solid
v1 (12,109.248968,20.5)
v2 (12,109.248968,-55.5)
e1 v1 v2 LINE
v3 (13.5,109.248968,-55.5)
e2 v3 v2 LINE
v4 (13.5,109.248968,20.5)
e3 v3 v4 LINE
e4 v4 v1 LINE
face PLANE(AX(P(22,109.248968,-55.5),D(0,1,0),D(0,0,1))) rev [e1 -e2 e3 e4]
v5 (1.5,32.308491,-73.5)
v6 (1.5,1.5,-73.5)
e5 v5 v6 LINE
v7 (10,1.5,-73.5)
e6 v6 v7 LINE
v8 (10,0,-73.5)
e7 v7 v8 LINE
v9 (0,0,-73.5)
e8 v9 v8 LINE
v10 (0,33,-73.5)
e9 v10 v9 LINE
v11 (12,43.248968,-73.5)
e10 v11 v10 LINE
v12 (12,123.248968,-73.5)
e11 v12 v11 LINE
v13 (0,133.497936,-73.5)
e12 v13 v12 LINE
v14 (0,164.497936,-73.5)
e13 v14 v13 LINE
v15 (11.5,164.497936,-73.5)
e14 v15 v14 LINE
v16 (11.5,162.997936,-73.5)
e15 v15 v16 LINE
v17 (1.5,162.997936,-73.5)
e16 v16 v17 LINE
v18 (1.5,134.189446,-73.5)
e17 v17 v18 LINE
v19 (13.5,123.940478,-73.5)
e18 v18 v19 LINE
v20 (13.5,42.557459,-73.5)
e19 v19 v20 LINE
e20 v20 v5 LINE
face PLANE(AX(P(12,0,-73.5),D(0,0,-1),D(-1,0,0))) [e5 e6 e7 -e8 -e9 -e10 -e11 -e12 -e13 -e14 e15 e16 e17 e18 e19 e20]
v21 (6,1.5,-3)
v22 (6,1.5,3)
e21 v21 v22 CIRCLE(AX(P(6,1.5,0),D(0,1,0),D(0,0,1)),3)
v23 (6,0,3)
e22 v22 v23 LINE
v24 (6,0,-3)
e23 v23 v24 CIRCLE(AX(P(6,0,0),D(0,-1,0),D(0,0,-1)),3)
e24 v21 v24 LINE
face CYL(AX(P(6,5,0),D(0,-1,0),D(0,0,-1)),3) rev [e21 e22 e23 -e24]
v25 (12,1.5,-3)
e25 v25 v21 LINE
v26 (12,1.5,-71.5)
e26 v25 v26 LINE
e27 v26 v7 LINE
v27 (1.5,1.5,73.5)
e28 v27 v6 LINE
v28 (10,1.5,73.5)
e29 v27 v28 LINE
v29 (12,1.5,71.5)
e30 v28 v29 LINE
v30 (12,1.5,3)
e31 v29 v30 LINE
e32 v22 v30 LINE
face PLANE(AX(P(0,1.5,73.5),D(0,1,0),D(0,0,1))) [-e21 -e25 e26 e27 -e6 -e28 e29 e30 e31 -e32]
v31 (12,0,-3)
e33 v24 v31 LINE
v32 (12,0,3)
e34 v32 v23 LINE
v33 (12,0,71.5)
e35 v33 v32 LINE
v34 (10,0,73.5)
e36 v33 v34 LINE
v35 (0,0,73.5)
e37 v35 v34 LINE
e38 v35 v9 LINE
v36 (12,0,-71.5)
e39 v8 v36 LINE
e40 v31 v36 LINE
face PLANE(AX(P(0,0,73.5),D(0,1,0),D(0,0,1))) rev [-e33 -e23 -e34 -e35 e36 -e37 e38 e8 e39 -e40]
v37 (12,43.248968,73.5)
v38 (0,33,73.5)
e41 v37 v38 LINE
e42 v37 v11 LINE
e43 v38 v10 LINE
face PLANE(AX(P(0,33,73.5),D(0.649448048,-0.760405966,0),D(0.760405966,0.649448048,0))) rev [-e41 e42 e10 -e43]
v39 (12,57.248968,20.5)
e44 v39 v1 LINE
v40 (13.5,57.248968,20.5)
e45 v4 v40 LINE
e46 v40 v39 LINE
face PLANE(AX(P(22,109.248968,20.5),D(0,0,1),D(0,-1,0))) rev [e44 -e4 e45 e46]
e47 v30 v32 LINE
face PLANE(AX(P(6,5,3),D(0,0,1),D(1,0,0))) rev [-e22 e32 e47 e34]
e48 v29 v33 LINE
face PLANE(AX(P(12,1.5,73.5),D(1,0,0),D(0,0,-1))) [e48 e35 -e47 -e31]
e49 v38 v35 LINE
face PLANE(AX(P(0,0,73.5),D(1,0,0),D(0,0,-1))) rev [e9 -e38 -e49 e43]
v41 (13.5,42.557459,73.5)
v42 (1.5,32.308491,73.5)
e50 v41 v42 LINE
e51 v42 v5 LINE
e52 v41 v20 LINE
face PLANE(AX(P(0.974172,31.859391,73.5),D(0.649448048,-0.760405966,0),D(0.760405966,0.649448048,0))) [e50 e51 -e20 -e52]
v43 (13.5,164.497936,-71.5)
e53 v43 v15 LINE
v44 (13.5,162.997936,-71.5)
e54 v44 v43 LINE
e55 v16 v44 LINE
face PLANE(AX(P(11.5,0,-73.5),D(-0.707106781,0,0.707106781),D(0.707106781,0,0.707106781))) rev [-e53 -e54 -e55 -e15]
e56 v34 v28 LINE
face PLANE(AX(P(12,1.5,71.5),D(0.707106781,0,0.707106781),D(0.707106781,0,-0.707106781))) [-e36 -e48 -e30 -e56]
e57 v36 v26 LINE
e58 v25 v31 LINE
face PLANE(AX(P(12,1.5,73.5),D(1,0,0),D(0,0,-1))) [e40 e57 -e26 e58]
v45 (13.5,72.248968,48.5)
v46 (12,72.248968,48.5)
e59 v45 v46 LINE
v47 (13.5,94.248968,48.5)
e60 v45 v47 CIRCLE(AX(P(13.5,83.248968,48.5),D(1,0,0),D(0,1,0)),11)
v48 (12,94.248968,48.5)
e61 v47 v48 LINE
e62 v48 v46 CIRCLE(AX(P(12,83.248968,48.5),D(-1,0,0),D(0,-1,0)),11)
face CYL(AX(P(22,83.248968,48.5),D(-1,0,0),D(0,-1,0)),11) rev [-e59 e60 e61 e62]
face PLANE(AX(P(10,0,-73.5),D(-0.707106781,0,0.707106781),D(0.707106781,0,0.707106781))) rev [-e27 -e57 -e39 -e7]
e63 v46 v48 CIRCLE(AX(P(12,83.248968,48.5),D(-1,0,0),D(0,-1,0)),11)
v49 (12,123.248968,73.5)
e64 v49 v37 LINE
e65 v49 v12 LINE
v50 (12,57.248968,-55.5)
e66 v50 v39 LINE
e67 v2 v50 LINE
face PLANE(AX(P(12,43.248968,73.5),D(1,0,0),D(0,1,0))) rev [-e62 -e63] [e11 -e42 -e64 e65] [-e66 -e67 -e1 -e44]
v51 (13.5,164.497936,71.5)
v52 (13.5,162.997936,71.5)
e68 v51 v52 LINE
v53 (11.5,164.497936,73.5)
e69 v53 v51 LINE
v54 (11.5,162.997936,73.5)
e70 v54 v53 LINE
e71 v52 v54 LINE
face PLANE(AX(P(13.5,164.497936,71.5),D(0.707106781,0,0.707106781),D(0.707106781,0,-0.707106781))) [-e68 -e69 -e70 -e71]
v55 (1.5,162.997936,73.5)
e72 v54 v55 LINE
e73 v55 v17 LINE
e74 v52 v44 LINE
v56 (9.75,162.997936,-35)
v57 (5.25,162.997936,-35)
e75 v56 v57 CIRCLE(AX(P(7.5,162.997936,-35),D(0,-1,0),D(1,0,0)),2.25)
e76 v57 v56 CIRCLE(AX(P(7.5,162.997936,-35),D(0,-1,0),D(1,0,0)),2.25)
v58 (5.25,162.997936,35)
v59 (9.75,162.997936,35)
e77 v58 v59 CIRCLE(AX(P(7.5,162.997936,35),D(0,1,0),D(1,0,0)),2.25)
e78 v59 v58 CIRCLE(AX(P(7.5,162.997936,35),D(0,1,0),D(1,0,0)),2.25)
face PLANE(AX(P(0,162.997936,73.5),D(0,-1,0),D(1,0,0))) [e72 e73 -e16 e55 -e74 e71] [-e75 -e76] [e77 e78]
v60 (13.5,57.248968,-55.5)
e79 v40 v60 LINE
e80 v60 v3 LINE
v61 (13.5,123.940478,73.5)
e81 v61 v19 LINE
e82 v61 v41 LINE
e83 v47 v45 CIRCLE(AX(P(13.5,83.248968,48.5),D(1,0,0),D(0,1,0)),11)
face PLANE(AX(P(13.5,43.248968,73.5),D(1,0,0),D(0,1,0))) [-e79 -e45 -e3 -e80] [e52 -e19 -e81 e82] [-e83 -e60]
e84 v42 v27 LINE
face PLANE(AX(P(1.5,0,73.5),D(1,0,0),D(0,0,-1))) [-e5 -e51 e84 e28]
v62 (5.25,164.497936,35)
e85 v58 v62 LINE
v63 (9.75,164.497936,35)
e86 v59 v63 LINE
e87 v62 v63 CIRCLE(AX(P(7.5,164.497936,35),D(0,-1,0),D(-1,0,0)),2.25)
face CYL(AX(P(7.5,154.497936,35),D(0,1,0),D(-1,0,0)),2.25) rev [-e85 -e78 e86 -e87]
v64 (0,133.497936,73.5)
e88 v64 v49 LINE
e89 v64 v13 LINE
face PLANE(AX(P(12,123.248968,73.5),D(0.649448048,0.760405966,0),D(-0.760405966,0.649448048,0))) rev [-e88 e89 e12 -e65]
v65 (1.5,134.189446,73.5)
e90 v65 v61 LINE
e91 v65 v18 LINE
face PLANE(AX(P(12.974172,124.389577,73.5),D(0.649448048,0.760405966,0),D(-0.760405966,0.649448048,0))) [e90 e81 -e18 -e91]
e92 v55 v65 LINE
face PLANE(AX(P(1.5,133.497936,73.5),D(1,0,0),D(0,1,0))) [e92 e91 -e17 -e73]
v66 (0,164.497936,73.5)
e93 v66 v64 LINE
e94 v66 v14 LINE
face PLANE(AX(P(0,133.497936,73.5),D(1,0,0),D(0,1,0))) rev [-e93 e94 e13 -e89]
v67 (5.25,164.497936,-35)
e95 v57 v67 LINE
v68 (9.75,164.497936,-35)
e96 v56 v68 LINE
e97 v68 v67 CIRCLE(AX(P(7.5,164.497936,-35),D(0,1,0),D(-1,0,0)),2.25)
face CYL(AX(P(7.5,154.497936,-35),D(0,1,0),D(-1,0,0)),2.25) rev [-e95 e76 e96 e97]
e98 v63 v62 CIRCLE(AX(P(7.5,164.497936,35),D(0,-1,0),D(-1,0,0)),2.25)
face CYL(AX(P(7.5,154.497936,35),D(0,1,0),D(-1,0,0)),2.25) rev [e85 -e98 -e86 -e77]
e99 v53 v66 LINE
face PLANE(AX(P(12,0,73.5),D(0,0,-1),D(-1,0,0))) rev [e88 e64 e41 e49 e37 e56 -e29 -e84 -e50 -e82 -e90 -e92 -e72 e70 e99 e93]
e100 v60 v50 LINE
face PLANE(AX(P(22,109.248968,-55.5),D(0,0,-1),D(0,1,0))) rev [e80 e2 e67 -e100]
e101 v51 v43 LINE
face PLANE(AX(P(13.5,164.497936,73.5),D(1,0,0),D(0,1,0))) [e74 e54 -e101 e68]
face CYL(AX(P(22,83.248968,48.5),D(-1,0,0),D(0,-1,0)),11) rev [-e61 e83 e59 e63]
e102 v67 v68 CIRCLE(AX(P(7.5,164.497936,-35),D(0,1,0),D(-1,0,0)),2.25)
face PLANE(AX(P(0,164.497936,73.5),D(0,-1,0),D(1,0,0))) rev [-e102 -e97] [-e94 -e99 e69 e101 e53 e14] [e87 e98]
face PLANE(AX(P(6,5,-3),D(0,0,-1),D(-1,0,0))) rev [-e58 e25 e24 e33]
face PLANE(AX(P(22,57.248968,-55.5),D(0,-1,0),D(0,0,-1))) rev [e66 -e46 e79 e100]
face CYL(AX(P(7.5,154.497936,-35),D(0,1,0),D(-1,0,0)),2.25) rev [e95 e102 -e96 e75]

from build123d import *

# Parameters (mm, degrees)
EXTRUDE_THIN1_DEPTH = 73.5
SKETCH2_W           = 76
SKETCH2_H           = 52
CUT_EXTRUDE1_DEPTH  = 10
CHAMFER1_SIZE       = 2
CUT_EXTRUDE3_DEPTH  = 5
SKETCH7_R           = 11
CUT_EXTRUDE4_DEPTH  = 10
SKETCH8_R           = 2.25
CUT_EXTRUDE5_DEPTH  = 10


with BuildPart() as part:
    # Sketch1 → Extrude-Thin1 (new, symmetric)
    with BuildSketch(Plane.XY):
        Polygon((12, 0), (0, 0), (0, 33), (12, 43.248968226), (12, 123.248968226), (0, 133.497936451), (0, 164.497936451), (13.5, 164.497936451), (13.5, 162.997936451), (1.5, 162.997936451), (1.5, 134.189445923), (13.5, 123.940477697), (13.5, 42.557458754), (1.5, 32.308490528), (1.5, 1.5), (12, 1.5), align=None)
    extrude(amount=EXTRUDE_THIN1_DEPTH, both=True)

    # Sketch2 → Cut-Extrude1 (cut)
    with BuildSketch(Plane.ZY.offset(-12)):
        with Locations((-17.5, 83.248968226)):
            Rectangle(SKETCH2_W, SKETCH2_H)
    extrude(amount=-CUT_EXTRUDE1_DEPTH, mode=Mode.SUBTRACT)

    # Chamfer1
    chamfer1_edges = [part.edges().sort_by_distance(p)[0] for p in [
        (13.5, 163.747936451, -73.5),
        (12, 0.75, -73.5),
        (13.5, 163.747936451, 73.5),
        (12, 0.75, 73.5),
    ]]
    chamfer(chamfer1_edges, length=CHAMFER1_SIZE)

    # Sketch6 → Cut-Extrude3 (cut)
    with BuildSketch(Plane.XZ):
        with BuildLine():
            Line((6, 3), (12, 3))
            ThreePointArc((12, 3), (15, 0), (12, -3))
            Line((12, -3), (6, -3))
            ThreePointArc((6, -3), (3, 0), (6, 3))
        make_face()
    extrude(amount=-CUT_EXTRUDE3_DEPTH, mode=Mode.SUBTRACT)

    # Sketch7 → Cut-Extrude4 (cut)
    with BuildSketch(Plane.ZY.offset(-12)):
        with Locations(Location((48.5, 83.248968226, 0), (0, 0, 270))):
            Circle(SKETCH7_R)
    extrude(amount=-CUT_EXTRUDE4_DEPTH, mode=Mode.SUBTRACT)

    # Sketch8 → Cut-Extrude5 (cut)
    with BuildSketch(Plane(origin=(0, 164.497936451, 0), x_dir=(1, 0, 0), z_dir=(0, 1, 0))):
        with Locations(Location((7.5, 35, 0), (0, 0, 180))):
            Circle(SKETCH8_R)
    cut_extrude5 = extrude(amount=-CUT_EXTRUDE5_DEPTH, mode=Mode.SUBTRACT)

    # Mirror1: Cut-Extrude5 across plane
    add(cut_extrude5.mirror(Plane.XY), mode=Mode.SUBTRACT)


solid = part.part
